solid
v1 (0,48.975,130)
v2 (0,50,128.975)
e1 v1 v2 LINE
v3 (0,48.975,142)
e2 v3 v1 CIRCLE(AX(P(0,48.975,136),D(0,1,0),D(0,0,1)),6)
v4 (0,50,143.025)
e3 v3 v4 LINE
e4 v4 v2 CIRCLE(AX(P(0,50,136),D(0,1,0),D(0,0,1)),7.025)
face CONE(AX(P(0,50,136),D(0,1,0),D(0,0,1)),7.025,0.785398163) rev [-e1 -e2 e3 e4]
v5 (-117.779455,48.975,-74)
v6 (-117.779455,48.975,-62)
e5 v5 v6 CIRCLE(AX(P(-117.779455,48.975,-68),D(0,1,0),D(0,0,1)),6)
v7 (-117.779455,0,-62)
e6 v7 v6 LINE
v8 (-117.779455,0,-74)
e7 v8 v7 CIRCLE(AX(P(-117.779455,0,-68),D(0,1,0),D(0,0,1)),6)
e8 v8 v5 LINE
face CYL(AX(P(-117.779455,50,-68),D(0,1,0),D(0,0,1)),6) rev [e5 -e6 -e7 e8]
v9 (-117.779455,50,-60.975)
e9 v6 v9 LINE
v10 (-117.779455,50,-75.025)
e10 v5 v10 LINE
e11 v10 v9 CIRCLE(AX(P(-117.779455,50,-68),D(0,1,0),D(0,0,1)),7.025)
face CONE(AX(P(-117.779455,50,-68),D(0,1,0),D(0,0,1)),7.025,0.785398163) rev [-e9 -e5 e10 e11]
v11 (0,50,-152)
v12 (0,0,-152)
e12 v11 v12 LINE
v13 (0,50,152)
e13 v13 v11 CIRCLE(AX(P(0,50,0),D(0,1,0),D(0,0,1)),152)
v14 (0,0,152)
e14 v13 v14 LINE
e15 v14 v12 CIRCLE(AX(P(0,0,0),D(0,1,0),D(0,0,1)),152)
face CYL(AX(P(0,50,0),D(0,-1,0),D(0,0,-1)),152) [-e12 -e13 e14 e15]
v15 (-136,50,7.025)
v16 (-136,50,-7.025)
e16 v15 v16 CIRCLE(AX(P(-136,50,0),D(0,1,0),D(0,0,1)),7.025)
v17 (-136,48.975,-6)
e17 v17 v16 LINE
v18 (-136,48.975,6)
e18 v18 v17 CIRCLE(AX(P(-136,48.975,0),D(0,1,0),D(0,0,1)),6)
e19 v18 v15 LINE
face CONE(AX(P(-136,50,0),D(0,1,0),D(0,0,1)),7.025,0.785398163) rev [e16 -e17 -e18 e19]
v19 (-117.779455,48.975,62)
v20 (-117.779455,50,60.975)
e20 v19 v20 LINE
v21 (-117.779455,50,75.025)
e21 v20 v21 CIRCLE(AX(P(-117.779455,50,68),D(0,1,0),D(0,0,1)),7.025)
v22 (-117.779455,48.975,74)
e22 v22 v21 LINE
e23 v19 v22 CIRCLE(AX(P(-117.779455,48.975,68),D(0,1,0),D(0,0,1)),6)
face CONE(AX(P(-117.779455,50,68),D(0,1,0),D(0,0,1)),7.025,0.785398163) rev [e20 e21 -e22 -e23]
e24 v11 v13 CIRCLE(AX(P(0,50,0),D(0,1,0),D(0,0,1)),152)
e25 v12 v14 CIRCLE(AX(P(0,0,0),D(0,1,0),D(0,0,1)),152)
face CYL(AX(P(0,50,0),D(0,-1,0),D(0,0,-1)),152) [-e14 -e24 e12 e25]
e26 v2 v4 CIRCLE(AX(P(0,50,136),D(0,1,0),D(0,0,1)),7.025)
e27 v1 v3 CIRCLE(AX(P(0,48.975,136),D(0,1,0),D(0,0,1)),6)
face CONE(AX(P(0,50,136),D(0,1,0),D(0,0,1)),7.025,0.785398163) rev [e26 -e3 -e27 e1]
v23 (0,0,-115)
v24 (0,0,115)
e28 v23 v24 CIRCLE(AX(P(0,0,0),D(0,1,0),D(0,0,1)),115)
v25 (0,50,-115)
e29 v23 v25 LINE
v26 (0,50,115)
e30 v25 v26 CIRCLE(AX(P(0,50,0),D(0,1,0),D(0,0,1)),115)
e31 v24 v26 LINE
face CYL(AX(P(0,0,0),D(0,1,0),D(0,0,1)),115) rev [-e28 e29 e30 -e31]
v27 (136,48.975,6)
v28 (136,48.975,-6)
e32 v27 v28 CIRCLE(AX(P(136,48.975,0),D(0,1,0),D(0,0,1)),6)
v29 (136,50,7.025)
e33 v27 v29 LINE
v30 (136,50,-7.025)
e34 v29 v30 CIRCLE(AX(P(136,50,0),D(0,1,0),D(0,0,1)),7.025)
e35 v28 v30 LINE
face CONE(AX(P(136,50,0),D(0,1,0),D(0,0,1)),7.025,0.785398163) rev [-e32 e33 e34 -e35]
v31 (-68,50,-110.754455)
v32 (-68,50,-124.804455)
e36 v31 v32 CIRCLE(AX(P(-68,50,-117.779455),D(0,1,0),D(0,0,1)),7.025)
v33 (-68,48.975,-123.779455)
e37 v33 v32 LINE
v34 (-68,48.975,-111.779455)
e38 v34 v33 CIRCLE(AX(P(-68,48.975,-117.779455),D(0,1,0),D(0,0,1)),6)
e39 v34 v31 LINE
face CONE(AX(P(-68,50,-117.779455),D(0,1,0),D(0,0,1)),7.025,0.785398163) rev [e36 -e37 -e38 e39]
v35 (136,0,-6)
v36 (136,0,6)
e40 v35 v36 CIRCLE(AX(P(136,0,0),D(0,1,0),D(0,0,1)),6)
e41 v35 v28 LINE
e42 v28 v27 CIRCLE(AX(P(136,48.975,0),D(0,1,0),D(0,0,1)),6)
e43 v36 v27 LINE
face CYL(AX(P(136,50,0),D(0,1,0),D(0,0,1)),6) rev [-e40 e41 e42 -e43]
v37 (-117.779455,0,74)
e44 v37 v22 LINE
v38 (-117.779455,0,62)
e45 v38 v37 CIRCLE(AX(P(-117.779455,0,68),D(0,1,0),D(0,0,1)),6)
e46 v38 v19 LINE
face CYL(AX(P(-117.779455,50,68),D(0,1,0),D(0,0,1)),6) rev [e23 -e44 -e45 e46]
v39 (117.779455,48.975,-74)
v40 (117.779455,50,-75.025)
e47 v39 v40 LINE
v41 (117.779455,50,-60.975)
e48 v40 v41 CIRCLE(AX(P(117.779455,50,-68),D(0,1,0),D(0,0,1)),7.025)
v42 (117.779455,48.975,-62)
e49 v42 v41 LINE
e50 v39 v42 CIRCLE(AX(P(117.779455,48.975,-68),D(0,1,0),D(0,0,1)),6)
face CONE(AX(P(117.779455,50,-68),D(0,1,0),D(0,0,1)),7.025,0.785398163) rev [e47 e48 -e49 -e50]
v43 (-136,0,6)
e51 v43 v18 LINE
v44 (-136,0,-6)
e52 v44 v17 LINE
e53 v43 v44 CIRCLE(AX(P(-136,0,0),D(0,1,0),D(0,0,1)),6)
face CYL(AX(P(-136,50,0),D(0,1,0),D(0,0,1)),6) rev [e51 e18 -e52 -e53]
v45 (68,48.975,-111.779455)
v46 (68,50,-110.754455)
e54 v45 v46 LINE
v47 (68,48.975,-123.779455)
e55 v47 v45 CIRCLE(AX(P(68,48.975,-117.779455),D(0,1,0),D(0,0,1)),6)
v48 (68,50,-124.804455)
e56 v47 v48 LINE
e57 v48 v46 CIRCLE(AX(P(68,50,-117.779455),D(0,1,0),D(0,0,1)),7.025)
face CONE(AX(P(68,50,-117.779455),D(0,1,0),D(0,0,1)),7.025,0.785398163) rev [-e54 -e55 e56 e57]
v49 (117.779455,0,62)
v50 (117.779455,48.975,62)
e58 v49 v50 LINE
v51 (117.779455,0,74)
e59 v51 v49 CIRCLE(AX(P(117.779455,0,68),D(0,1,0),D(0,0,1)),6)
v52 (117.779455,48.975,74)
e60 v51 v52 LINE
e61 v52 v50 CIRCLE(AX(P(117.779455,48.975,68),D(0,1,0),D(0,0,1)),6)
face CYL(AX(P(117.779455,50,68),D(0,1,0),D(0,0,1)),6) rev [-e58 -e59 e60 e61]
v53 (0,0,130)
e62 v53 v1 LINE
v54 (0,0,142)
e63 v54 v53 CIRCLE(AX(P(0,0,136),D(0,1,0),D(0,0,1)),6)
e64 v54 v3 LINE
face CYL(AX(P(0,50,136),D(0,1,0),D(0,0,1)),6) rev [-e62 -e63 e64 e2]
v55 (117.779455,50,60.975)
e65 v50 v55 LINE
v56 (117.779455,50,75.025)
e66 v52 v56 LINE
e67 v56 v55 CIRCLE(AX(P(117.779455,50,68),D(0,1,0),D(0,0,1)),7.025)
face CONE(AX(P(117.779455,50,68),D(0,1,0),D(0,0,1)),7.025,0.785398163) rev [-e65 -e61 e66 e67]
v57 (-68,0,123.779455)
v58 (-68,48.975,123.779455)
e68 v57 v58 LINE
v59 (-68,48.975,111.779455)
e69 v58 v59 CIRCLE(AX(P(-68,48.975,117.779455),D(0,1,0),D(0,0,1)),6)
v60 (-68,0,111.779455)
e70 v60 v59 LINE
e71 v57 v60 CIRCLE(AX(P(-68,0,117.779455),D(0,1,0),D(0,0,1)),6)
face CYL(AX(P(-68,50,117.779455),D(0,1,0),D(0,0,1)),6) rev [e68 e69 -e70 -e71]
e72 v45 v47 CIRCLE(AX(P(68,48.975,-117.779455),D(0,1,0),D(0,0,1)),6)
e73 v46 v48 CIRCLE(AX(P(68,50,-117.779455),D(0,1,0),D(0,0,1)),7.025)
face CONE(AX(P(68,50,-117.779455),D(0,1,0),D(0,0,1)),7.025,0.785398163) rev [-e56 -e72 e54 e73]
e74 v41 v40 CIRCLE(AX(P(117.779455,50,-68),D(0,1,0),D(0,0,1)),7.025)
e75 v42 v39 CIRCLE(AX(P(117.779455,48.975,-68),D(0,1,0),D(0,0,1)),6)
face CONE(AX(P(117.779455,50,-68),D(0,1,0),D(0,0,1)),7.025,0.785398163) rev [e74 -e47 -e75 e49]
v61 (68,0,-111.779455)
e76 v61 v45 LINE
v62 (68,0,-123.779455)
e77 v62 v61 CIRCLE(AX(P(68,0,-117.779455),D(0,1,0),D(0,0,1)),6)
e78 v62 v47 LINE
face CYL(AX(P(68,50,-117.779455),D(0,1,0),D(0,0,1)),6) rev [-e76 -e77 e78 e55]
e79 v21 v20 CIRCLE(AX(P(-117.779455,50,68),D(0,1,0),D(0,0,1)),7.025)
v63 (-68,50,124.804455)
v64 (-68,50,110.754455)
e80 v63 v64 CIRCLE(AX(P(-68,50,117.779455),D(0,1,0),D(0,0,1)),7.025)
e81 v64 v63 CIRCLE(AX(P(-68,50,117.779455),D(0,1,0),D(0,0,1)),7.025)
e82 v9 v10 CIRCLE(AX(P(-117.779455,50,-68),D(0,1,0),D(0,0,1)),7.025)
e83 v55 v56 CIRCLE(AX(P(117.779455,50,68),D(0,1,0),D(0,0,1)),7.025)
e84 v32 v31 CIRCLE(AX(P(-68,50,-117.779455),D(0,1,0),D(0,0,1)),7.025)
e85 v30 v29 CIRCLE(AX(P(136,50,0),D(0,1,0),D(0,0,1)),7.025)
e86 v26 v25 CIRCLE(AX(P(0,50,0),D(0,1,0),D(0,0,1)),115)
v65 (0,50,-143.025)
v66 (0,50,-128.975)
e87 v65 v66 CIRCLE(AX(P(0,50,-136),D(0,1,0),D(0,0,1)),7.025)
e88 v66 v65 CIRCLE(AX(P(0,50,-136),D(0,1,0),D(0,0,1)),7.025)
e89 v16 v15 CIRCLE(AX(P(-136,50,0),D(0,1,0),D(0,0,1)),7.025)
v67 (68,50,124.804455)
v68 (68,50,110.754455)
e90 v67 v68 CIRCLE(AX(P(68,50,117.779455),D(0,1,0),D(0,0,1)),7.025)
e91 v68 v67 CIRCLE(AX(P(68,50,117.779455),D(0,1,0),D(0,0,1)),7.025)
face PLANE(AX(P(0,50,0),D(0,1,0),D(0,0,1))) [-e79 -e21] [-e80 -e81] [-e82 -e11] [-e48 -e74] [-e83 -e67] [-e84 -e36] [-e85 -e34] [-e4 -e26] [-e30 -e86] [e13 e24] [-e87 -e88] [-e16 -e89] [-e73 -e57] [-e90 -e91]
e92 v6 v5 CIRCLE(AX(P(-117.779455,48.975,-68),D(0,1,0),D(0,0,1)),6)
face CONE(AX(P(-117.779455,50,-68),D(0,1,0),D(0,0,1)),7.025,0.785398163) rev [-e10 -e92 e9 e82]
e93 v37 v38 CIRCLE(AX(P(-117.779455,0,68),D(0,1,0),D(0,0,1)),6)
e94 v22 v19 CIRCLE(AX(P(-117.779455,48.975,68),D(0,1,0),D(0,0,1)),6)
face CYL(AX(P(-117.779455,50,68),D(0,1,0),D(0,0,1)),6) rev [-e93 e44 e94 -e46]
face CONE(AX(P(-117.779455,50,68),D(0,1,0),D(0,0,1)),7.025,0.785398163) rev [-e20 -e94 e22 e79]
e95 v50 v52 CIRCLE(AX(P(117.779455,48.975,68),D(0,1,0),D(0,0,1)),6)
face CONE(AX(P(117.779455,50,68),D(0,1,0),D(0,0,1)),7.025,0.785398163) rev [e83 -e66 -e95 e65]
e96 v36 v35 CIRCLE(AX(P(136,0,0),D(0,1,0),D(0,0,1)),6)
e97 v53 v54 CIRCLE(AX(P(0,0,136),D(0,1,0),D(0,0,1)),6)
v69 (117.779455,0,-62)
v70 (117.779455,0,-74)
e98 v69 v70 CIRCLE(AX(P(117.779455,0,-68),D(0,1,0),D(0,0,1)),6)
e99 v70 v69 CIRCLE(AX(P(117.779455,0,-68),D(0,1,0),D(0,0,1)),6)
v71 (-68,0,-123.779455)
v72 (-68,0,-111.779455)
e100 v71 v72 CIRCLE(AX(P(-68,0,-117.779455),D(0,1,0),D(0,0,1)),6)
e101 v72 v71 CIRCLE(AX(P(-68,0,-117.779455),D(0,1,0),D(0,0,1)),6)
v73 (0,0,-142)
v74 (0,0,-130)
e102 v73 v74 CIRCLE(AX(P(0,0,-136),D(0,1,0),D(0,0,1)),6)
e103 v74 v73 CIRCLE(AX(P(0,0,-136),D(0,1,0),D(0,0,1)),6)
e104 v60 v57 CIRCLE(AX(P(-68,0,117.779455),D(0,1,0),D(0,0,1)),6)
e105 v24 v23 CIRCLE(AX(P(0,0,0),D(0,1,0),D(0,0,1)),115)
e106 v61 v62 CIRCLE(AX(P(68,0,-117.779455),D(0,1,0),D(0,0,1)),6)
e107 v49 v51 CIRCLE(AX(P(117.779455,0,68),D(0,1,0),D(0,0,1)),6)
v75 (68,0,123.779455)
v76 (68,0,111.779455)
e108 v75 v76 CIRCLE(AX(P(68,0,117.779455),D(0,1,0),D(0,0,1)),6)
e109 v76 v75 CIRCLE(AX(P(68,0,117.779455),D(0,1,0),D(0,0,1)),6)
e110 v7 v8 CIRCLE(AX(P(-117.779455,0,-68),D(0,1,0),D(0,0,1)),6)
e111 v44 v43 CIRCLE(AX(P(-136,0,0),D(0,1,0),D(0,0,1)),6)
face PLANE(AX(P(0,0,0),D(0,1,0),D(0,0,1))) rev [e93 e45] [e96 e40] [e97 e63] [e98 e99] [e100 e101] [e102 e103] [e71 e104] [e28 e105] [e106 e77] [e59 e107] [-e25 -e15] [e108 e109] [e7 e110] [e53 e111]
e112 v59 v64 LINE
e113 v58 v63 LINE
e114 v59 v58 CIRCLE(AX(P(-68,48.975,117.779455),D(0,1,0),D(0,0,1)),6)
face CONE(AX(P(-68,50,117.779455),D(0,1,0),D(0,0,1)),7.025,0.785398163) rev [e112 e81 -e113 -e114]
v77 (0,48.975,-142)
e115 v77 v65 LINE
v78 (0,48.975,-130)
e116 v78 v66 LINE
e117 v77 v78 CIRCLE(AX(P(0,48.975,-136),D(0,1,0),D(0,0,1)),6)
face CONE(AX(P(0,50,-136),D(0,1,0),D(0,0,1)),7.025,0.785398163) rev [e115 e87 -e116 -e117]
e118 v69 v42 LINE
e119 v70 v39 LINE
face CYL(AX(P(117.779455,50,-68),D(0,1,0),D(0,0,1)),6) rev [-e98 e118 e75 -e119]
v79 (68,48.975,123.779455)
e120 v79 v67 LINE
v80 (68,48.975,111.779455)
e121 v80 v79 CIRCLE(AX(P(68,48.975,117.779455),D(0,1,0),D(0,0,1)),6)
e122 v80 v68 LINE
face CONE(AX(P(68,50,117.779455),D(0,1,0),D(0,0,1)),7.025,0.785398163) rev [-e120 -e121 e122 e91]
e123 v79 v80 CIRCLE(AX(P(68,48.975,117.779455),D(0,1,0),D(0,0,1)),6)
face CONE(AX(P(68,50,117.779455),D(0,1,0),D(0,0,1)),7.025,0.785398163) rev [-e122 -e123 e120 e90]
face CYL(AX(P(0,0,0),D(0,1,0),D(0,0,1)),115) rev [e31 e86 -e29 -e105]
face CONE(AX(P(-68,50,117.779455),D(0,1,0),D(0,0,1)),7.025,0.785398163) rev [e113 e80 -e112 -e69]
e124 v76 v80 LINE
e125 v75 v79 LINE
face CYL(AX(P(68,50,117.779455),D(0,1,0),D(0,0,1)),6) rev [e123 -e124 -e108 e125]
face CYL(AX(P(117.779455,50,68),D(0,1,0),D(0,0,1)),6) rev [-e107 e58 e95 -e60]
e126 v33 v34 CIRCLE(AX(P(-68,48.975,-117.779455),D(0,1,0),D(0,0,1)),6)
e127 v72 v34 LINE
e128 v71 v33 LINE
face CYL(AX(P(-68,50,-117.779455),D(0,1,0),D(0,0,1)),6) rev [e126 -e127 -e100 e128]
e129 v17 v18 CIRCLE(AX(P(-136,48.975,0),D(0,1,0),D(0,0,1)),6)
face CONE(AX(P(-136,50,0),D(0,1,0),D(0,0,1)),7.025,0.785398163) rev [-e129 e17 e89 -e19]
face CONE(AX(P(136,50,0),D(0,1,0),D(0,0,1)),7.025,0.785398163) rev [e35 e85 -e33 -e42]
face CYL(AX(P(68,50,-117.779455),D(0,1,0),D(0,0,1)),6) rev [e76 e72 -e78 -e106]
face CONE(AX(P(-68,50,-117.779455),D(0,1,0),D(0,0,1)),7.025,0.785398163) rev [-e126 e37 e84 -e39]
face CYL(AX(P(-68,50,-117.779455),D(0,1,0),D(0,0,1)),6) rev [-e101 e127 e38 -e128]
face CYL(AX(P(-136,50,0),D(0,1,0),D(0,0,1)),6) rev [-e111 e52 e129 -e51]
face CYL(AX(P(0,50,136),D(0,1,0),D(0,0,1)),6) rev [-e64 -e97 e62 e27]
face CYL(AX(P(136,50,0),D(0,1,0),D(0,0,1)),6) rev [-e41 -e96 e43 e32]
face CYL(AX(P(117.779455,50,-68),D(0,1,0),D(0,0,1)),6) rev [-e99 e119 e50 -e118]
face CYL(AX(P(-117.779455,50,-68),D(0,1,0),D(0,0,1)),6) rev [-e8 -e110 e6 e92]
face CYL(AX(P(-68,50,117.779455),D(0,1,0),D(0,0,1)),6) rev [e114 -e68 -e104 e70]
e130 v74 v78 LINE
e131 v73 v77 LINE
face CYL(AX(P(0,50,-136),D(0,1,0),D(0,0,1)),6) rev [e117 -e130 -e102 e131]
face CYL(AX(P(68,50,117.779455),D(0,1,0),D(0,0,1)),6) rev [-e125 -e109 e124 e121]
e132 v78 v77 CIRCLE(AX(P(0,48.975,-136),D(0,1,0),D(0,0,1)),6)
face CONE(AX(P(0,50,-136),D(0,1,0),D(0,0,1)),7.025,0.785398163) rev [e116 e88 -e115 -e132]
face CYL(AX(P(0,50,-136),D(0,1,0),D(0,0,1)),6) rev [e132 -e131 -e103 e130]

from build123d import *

# Parameters (mm, degrees)
SKETCH1_R                    = 152
BOSS_EXTRUDE1_DEPTH          = 50
M14_TAPPED_HOLE1_D           = 12
M14_TAPPED_HOLE1_CSINK_D     = 14.05
M14_TAPPED_HOLE1_CSINK_ANGLE = 90
SKETCH4_R                    = 115
BOSS_EXTRUDE2_DEPTH          = 5
M14_TAPPED_HOLE2_D           = 12
M14_TAPPED_HOLE2_CSINK_D     = 14.05
M14_TAPPED_HOLE2_CSINK_ANGLE = 90
SKETCH8_R                    = 115
CUT_EXTRUDE1_DEPTH           = 222.885105404


with BuildPart() as part:
    # Sketch1 → Boss-Extrude1 (new body)
    with BuildSketch(Plane(origin=(0, 0, 0), x_dir=(1, 0, 0), z_dir=(0, 1, 0))):
        with Locations(Location((0, 0, 0), (0, 0, 270))):
            Circle(SKETCH1_R)
    extrude(amount=BOSS_EXTRUDE1_DEPTH)

    # M14 Tapped Hole1 (through all)
    with Locations(Plane(origin=(0, 50, 0), x_dir=(1, 0, 0), z_dir=(0, 1, 0))):
        with Locations((-68, 117.779454915), (0, 136), (68, 117.779454915), (117.779454915, 68), (136, 0), (117.779454915, -68), (68, -117.779454915), (0, -136), (-68, -117.779454915), (-117.779454915, -68), (-136, 0), (-117.779454915, 68)):
            CounterSinkHole(M14_TAPPED_HOLE1_D / 2, M14_TAPPED_HOLE1_CSINK_D / 2, counter_sink_angle=M14_TAPPED_HOLE1_CSINK_ANGLE)

    # Sketch4 → Boss-Extrude2 (add)
    with BuildSketch(Plane(origin=(0, 50, 0), x_dir=(1, 0, 0), z_dir=(0, 1, 0))):
        with Locations(Location((0, 0, 0), (0, 0, 270))):
            Circle(SKETCH4_R)
    extrude(amount=BOSS_EXTRUDE2_DEPTH)

    # M14 Tapped Hole2 (through all)
    with Locations(Plane(origin=(0, 55, 0), x_dir=(1, 0, 0), z_dir=(0, 1, 0))):
        with Locations((-44, 76.210235533), (0, 88), (44, 76.210235533), (76.210235533, 44), (88, 0), (76.210235533, -44), (44, -76.210235533), (0, -88), (-44, -76.210235533), (-76.210235533, -44), (-88, 0), (-76.210235533, 44)):
            CounterSinkHole(M14_TAPPED_HOLE2_D / 2, M14_TAPPED_HOLE2_CSINK_D / 2, counter_sink_angle=M14_TAPPED_HOLE2_CSINK_ANGLE)

    # Sketch8 → Cut-Extrude1 (cut, through all)
    with BuildSketch(Plane(origin=(0, 55, 0), x_dir=(1, 0, 0), z_dir=(0, 1, 0))):
        with Locations(Location((0, 0, 0), (0, 0, 270))):
            Circle(SKETCH8_R)
    extrude(amount=-CUT_EXTRUDE1_DEPTH, mode=Mode.SUBTRACT)


solid = part.part
